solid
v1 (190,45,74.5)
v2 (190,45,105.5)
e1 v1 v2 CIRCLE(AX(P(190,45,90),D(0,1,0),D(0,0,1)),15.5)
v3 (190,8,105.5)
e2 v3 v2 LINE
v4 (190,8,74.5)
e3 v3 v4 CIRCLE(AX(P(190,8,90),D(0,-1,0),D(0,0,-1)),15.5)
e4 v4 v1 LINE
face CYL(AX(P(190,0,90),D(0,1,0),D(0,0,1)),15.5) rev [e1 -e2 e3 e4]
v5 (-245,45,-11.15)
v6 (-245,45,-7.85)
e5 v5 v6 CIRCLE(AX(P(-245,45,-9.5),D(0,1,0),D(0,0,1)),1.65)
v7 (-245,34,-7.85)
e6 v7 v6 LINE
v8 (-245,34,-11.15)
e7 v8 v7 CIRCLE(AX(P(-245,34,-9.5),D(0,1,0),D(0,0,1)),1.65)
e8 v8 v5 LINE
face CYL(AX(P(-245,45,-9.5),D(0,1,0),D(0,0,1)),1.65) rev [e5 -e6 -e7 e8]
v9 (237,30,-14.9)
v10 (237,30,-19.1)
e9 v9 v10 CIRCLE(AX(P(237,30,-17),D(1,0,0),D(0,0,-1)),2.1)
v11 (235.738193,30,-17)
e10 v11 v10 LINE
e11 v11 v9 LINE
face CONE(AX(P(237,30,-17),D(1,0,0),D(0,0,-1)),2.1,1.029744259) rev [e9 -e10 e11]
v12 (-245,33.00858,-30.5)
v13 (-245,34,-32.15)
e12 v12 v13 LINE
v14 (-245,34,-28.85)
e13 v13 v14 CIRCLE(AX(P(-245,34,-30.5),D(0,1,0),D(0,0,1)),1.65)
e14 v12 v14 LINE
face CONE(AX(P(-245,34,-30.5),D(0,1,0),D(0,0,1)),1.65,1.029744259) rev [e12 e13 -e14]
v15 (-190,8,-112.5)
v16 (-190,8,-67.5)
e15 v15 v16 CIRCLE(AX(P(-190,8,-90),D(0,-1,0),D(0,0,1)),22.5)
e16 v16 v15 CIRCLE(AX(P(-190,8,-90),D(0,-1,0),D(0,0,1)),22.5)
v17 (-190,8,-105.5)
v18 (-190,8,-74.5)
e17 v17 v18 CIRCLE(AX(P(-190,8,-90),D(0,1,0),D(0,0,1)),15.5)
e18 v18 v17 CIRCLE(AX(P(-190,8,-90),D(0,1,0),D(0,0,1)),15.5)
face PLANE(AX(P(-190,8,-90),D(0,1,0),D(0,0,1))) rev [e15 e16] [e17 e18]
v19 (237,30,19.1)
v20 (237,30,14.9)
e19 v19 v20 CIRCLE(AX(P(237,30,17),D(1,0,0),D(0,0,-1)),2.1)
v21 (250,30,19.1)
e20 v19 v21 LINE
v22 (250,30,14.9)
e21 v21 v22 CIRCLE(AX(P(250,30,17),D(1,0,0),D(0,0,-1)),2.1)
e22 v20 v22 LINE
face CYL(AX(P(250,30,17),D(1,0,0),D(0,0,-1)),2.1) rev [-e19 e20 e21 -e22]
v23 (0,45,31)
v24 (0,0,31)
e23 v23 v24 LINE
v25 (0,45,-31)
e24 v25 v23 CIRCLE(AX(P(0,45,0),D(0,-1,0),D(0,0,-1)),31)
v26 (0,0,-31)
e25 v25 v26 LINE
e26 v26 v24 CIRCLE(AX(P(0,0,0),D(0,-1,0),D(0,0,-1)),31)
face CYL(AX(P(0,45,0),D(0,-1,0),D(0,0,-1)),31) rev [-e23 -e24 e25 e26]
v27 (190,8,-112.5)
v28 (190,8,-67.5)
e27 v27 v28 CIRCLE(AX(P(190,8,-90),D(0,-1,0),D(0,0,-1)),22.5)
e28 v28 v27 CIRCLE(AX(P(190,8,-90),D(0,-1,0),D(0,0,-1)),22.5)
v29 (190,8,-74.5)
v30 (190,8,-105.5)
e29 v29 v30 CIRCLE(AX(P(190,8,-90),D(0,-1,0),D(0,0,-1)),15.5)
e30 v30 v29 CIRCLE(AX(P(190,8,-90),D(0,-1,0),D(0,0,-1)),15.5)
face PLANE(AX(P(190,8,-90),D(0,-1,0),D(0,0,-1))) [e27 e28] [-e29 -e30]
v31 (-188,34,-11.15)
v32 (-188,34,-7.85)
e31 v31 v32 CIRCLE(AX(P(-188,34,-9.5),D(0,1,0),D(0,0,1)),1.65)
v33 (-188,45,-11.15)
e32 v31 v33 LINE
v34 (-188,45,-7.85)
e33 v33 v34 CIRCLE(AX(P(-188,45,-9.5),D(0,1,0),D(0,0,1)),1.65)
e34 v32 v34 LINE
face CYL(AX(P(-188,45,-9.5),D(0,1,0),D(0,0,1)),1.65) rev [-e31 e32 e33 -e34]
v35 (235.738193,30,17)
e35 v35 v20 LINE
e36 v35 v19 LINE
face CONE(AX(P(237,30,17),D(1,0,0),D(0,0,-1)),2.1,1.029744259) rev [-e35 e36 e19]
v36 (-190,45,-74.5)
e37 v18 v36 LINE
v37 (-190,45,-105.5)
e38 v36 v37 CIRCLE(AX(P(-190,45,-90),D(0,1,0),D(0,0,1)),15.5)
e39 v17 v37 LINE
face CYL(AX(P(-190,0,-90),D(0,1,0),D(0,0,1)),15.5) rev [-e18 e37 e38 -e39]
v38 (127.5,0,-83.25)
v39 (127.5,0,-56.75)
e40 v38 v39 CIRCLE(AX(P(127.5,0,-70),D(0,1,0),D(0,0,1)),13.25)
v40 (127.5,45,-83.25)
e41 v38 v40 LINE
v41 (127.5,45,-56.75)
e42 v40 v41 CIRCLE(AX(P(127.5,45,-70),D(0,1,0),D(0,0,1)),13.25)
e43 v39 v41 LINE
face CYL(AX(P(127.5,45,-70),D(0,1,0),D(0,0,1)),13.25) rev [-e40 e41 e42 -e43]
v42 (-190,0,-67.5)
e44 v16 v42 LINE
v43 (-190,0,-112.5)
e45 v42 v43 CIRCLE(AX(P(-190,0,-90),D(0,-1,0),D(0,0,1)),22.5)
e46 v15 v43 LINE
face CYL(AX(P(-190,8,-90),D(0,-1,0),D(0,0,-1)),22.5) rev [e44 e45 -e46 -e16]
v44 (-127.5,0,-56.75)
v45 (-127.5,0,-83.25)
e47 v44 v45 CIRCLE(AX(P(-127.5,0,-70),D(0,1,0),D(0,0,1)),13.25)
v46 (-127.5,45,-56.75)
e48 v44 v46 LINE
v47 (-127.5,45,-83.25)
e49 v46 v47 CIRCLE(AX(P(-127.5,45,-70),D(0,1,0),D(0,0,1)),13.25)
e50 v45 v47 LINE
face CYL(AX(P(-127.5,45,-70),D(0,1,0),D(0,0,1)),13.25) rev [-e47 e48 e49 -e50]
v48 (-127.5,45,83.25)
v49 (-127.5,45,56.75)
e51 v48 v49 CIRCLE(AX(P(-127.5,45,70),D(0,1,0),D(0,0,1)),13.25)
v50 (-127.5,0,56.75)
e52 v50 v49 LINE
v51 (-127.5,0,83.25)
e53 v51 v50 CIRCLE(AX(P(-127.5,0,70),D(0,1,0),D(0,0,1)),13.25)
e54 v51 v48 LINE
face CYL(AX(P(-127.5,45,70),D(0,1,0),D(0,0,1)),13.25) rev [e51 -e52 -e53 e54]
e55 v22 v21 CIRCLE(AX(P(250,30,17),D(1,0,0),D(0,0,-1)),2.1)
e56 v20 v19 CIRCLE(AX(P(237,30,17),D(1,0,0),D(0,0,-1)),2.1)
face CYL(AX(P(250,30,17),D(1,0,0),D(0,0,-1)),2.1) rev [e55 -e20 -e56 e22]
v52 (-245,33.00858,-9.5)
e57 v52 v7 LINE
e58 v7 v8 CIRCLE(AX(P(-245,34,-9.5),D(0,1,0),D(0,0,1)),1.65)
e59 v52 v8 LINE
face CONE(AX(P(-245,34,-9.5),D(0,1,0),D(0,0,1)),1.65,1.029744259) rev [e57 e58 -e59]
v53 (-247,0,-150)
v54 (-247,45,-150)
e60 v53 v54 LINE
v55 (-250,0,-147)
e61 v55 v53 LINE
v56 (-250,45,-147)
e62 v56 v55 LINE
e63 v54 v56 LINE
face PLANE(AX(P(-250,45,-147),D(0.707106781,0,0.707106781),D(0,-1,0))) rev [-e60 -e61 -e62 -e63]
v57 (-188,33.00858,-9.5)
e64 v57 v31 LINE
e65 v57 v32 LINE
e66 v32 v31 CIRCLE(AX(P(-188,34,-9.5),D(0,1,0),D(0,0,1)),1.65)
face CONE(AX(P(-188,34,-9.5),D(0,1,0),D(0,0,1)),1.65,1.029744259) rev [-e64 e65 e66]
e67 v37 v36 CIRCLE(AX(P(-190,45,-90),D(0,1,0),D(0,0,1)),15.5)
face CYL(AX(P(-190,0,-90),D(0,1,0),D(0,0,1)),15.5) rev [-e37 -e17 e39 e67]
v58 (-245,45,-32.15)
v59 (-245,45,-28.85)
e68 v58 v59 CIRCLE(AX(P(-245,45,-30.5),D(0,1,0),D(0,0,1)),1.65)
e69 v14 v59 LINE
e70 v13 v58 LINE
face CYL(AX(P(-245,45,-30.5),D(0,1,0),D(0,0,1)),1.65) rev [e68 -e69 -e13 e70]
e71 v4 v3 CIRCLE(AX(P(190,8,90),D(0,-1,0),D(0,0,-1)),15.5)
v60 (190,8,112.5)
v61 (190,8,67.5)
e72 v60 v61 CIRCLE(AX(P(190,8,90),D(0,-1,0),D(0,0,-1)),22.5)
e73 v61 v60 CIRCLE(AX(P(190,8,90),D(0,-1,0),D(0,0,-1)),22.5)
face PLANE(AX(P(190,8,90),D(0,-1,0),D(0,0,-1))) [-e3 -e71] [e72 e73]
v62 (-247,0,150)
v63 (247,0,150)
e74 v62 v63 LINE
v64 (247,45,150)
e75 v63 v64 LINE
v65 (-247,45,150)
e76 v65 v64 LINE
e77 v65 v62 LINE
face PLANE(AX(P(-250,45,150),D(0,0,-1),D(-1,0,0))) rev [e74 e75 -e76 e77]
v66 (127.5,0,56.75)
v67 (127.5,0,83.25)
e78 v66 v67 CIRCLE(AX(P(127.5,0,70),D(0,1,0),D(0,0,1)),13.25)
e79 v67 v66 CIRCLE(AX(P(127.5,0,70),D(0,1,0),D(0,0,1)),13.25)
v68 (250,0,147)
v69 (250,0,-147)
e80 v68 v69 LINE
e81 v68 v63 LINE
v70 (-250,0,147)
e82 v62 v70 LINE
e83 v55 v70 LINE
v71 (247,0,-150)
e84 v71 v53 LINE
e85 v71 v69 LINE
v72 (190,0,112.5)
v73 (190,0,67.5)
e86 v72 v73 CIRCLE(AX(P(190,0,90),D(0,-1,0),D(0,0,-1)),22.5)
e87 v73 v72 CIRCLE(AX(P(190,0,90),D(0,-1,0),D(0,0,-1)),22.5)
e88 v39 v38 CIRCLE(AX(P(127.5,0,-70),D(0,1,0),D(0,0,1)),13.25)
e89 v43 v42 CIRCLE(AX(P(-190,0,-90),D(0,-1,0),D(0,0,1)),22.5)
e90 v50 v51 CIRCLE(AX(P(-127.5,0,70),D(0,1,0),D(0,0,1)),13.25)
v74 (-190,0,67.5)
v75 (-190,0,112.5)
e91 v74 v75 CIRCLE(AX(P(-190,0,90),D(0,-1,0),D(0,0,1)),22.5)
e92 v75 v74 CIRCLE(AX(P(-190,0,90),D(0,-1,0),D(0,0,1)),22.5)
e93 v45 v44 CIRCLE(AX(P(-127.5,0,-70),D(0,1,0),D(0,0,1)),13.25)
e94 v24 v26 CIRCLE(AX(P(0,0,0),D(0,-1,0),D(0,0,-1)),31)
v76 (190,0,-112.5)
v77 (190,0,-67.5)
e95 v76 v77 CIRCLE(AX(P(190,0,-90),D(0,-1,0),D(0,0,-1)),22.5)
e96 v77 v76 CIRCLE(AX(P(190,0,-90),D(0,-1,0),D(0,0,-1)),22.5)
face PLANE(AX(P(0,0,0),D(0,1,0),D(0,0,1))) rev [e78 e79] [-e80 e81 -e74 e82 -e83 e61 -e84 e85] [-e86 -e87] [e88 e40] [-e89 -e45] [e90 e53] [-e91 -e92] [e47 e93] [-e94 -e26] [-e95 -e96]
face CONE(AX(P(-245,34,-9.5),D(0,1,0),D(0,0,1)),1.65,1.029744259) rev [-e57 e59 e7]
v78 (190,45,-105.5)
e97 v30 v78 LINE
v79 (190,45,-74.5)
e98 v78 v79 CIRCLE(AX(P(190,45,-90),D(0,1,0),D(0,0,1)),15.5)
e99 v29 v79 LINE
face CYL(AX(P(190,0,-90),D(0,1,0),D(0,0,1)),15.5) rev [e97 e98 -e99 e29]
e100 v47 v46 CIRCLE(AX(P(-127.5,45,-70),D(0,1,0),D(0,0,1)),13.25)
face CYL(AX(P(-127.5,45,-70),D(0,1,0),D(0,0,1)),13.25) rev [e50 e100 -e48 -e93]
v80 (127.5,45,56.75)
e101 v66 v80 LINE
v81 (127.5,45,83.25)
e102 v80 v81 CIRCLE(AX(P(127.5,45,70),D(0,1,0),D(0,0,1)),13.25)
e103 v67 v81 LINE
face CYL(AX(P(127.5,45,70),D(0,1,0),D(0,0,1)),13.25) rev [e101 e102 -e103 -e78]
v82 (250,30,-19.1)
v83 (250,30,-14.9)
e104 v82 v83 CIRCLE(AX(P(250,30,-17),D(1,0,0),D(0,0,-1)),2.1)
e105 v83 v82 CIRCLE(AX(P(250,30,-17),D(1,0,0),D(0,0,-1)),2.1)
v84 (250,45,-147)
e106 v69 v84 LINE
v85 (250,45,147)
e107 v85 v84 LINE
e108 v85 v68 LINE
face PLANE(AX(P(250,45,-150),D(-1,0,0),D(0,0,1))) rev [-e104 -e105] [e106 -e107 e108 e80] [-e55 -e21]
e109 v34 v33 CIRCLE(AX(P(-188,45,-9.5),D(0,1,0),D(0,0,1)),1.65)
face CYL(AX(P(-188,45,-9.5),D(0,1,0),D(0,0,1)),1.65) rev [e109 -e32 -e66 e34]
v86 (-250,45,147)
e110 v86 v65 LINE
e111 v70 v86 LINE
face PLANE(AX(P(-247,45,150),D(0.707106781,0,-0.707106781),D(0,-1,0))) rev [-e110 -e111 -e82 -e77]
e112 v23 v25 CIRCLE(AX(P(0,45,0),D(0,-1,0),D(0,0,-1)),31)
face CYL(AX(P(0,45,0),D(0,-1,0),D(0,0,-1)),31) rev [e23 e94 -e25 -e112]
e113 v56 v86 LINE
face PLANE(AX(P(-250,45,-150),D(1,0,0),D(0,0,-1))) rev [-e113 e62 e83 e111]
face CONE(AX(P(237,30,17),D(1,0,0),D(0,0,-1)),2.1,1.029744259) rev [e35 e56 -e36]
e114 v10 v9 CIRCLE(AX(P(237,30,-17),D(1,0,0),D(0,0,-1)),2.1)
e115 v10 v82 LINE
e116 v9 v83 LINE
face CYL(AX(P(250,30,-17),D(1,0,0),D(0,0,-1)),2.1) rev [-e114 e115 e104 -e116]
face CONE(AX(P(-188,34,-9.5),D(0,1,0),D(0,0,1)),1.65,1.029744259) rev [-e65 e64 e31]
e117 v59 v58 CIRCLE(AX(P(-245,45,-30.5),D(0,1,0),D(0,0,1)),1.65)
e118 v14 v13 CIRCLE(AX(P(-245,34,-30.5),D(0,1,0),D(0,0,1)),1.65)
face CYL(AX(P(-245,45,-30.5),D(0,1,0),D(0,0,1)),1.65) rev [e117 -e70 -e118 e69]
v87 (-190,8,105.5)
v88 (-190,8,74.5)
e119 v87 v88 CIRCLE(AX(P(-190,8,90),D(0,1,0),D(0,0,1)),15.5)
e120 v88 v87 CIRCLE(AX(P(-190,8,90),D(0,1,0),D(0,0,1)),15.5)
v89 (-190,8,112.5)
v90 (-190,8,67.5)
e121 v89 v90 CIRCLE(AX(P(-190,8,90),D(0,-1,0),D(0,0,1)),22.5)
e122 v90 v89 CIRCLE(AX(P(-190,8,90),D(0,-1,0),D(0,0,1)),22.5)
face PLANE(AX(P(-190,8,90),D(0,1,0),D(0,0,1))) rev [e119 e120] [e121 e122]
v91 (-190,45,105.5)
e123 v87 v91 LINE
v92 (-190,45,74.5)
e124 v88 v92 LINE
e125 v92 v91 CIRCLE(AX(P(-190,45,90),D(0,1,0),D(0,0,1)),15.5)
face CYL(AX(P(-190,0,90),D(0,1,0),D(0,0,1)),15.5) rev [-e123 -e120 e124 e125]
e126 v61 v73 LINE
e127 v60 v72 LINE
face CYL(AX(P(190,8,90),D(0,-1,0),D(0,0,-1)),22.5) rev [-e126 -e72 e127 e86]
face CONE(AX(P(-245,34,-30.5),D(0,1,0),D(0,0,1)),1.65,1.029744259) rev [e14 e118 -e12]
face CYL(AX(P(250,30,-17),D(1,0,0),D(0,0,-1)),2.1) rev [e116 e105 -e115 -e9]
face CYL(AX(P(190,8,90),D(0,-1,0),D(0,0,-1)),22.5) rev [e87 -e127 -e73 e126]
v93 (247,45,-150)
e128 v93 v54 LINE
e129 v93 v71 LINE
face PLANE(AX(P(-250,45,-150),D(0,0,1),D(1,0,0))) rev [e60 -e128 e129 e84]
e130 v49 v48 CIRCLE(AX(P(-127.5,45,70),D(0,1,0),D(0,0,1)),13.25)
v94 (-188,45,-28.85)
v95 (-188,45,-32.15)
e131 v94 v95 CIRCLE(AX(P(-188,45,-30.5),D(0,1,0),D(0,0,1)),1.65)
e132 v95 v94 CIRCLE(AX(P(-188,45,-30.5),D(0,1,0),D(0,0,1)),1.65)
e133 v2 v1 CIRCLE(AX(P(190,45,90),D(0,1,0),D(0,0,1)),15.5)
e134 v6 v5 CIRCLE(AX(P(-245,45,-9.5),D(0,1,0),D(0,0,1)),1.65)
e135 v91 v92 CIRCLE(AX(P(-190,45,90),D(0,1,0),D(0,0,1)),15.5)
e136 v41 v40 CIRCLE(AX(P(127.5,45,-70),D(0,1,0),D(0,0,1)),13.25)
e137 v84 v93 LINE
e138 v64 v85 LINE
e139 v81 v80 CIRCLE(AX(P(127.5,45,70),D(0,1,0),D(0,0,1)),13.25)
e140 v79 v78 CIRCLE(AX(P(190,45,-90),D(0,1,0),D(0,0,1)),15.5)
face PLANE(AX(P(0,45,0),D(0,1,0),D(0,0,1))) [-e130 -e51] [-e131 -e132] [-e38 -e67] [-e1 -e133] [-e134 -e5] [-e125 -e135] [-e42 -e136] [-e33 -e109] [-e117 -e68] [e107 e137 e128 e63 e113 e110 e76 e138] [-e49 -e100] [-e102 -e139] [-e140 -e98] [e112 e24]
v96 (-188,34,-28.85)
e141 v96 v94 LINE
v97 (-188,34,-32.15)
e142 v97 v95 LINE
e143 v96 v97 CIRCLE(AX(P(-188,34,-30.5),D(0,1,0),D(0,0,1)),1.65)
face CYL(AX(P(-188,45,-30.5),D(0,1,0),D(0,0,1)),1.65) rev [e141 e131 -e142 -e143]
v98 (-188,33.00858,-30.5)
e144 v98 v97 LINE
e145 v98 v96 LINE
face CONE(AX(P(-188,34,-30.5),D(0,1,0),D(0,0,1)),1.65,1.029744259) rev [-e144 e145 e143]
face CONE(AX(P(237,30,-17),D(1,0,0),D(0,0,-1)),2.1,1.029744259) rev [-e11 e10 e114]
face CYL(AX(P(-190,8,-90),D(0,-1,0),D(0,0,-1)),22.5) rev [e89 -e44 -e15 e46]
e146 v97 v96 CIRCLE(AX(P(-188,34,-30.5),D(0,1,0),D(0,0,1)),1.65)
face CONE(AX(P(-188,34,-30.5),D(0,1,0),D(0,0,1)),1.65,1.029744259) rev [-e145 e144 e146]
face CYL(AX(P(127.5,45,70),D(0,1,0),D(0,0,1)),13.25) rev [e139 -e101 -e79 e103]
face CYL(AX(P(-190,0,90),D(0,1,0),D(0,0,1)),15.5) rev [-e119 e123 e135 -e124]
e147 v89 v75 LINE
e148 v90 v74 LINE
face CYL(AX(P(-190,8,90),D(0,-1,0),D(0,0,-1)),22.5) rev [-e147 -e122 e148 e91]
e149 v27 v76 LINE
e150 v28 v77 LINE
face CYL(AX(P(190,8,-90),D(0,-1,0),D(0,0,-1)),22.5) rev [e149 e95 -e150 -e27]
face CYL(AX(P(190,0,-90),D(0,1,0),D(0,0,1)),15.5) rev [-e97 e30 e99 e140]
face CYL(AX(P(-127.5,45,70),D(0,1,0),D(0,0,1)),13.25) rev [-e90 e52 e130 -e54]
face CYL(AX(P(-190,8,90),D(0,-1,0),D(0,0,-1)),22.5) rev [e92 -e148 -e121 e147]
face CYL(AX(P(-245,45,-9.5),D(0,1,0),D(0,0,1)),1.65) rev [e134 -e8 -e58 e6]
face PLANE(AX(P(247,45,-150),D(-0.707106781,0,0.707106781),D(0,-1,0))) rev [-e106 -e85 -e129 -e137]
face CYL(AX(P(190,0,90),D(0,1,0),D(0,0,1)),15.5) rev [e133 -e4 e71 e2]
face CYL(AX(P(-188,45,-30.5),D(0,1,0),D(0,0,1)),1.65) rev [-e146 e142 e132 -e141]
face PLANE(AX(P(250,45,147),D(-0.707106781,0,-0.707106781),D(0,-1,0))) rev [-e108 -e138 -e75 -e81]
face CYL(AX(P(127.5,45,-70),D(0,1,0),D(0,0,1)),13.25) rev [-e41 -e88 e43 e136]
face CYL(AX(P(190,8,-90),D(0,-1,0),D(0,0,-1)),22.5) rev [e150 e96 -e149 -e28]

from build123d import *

# Parameters (mm, degrees)
SKETCH_1_W             = 500
SKETCH_1_H             = 300
EXTRUDE_1_DEPTH        = 45
SKETCH_2_R             = 22.5
CUT_EXTRUDE_1_DEPTH    = 8
CHAMFER_1_SIZE         = 3
SKETCH_16_R            = 15.5
CUT_EXTRUDE_3_DEPTH    = 296
SKETCH_17_R            = 31
CUT_EXTRUDE_4_DEPTH    = 296
HOLE_WIZARD_M4_1_D     = 3.3
HOLE_WIZARD_M4_1_DEPTH = 11
HOLE_WIZARD_M4_1_TIP   = 0.991420021
HOLE_WIZARD_M5_1_D     = 4.2
HOLE_WIZARD_M5_1_DEPTH = 13
HOLE_WIZARD_M5_1_TIP   = 1.2618073
HOLE_WIZARD_M30_1_D    = 26.5


with BuildPart() as part:
    # 草图1 → 凸台-拉伸1 (new body)
    with BuildSketch(Plane(origin=(0, 0, 0), x_dir=(1, 0, 0), z_dir=(0, 1, 0))):
        Rectangle(SKETCH_1_W, SKETCH_1_H)
    extrude(amount=EXTRUDE_1_DEPTH)

    # 草图2 → 切除-拉伸1 (cut)
    with BuildSketch(Plane.XZ):
        with Locations(Location((190, 90, 0), (0, 0, 270))):
            Circle(SKETCH_2_R)
        with Locations(Location((-190, 90, 0), (0, 0, 90))):
            Circle(SKETCH_2_R)
        with Locations(Location((190, -90, 0), (0, 0, 270))):
            Circle(SKETCH_2_R)
        with Locations(Location((-190, -90, 0), (0, 0, 90))):
            Circle(SKETCH_2_R)
    extrude(amount=-CUT_EXTRUDE_1_DEPTH, mode=Mode.SUBTRACT)

    # 倒角1
    chamfer_1_edges = [part.edges().sort_by_distance(p)[0] for p in [
        (250, 22.5, 150),
        (-250, 22.5, 150),
        (-250, 22.5, -150),
        (250, 22.5, -150),
    ]]
    chamfer(chamfer_1_edges, length=CHAMFER_1_SIZE)

    # 草图16 → 切除-拉伸3 (cut, through all)
    with BuildSketch(Plane(origin=(0, 45, 0), x_dir=(1, 0, 0), z_dir=(0, 1, 0))):
        with Locations(Location((190, -90, 0), (0, 0, 270))):
            Circle(SKETCH_16_R)
        with Locations(Location((190, 90, 0), (0, 0, 270))):
            Circle(SKETCH_16_R)
        with Locations(Location((-190, 90, 0), (0, 0, 270))):
            Circle(SKETCH_16_R)
        with Locations(Location((-190, -90, 0), (0, 0, 270))):
            Circle(SKETCH_16_R)
    extrude(amount=-CUT_EXTRUDE_3_DEPTH, mode=Mode.SUBTRACT)

    # 草图17 → 切除-拉伸4 (cut, through all)
    with BuildSketch(Plane.XZ):
        with Locations(Location((0, 0, 0), (0, 0, 270))):
            Circle(SKETCH_17_R)
    extrude(amount=-CUT_EXTRUDE_4_DEPTH, mode=Mode.SUBTRACT)

    # M4 螺纹孔1
    with Locations(Plane(origin=(0, 45, 0), x_dir=(1, 0, 0), z_dir=(0, 1, 0))):
        with Locations((-188, 30.5), (-245, 9.5), (-188, 9.5), (-245, 30.5)):
            Hole(HOLE_WIZARD_M4_1_D / 2, depth=HOLE_WIZARD_M4_1_DEPTH)
            with Locations((0, 0, -(HOLE_WIZARD_M4_1_DEPTH + HOLE_WIZARD_M4_1_TIP / 2))):  # 118° drill point
                Cone(0, HOLE_WIZARD_M4_1_D / 2, HOLE_WIZARD_M4_1_TIP, mode=Mode.SUBTRACT)

    # M5 螺纹孔1
    with Locations(Plane(origin=(250, 0, 0), x_dir=(0, 0, -1), z_dir=(1, 0, 0))):
        with Locations((-17, 30), (17, 30)):
            Hole(HOLE_WIZARD_M5_1_D / 2, depth=HOLE_WIZARD_M5_1_DEPTH)
            with Locations((0, 0, -(HOLE_WIZARD_M5_1_DEPTH + HOLE_WIZARD_M5_1_TIP / 2))):  # 118° drill point
                Cone(0, HOLE_WIZARD_M5_1_D / 2, HOLE_WIZARD_M5_1_TIP, mode=Mode.SUBTRACT)

    # M30 螺纹孔1 (through all)
    with Locations(Plane(origin=(0, 45, 0), x_dir=(1, 0, 0), z_dir=(0, 1, 0))):
        with Locations((-127.5, 70), (-127.5, -70), (127.5, 70), (127.5, -70)):
            Hole(HOLE_WIZARD_M30_1_D / 2)


solid = part.part
